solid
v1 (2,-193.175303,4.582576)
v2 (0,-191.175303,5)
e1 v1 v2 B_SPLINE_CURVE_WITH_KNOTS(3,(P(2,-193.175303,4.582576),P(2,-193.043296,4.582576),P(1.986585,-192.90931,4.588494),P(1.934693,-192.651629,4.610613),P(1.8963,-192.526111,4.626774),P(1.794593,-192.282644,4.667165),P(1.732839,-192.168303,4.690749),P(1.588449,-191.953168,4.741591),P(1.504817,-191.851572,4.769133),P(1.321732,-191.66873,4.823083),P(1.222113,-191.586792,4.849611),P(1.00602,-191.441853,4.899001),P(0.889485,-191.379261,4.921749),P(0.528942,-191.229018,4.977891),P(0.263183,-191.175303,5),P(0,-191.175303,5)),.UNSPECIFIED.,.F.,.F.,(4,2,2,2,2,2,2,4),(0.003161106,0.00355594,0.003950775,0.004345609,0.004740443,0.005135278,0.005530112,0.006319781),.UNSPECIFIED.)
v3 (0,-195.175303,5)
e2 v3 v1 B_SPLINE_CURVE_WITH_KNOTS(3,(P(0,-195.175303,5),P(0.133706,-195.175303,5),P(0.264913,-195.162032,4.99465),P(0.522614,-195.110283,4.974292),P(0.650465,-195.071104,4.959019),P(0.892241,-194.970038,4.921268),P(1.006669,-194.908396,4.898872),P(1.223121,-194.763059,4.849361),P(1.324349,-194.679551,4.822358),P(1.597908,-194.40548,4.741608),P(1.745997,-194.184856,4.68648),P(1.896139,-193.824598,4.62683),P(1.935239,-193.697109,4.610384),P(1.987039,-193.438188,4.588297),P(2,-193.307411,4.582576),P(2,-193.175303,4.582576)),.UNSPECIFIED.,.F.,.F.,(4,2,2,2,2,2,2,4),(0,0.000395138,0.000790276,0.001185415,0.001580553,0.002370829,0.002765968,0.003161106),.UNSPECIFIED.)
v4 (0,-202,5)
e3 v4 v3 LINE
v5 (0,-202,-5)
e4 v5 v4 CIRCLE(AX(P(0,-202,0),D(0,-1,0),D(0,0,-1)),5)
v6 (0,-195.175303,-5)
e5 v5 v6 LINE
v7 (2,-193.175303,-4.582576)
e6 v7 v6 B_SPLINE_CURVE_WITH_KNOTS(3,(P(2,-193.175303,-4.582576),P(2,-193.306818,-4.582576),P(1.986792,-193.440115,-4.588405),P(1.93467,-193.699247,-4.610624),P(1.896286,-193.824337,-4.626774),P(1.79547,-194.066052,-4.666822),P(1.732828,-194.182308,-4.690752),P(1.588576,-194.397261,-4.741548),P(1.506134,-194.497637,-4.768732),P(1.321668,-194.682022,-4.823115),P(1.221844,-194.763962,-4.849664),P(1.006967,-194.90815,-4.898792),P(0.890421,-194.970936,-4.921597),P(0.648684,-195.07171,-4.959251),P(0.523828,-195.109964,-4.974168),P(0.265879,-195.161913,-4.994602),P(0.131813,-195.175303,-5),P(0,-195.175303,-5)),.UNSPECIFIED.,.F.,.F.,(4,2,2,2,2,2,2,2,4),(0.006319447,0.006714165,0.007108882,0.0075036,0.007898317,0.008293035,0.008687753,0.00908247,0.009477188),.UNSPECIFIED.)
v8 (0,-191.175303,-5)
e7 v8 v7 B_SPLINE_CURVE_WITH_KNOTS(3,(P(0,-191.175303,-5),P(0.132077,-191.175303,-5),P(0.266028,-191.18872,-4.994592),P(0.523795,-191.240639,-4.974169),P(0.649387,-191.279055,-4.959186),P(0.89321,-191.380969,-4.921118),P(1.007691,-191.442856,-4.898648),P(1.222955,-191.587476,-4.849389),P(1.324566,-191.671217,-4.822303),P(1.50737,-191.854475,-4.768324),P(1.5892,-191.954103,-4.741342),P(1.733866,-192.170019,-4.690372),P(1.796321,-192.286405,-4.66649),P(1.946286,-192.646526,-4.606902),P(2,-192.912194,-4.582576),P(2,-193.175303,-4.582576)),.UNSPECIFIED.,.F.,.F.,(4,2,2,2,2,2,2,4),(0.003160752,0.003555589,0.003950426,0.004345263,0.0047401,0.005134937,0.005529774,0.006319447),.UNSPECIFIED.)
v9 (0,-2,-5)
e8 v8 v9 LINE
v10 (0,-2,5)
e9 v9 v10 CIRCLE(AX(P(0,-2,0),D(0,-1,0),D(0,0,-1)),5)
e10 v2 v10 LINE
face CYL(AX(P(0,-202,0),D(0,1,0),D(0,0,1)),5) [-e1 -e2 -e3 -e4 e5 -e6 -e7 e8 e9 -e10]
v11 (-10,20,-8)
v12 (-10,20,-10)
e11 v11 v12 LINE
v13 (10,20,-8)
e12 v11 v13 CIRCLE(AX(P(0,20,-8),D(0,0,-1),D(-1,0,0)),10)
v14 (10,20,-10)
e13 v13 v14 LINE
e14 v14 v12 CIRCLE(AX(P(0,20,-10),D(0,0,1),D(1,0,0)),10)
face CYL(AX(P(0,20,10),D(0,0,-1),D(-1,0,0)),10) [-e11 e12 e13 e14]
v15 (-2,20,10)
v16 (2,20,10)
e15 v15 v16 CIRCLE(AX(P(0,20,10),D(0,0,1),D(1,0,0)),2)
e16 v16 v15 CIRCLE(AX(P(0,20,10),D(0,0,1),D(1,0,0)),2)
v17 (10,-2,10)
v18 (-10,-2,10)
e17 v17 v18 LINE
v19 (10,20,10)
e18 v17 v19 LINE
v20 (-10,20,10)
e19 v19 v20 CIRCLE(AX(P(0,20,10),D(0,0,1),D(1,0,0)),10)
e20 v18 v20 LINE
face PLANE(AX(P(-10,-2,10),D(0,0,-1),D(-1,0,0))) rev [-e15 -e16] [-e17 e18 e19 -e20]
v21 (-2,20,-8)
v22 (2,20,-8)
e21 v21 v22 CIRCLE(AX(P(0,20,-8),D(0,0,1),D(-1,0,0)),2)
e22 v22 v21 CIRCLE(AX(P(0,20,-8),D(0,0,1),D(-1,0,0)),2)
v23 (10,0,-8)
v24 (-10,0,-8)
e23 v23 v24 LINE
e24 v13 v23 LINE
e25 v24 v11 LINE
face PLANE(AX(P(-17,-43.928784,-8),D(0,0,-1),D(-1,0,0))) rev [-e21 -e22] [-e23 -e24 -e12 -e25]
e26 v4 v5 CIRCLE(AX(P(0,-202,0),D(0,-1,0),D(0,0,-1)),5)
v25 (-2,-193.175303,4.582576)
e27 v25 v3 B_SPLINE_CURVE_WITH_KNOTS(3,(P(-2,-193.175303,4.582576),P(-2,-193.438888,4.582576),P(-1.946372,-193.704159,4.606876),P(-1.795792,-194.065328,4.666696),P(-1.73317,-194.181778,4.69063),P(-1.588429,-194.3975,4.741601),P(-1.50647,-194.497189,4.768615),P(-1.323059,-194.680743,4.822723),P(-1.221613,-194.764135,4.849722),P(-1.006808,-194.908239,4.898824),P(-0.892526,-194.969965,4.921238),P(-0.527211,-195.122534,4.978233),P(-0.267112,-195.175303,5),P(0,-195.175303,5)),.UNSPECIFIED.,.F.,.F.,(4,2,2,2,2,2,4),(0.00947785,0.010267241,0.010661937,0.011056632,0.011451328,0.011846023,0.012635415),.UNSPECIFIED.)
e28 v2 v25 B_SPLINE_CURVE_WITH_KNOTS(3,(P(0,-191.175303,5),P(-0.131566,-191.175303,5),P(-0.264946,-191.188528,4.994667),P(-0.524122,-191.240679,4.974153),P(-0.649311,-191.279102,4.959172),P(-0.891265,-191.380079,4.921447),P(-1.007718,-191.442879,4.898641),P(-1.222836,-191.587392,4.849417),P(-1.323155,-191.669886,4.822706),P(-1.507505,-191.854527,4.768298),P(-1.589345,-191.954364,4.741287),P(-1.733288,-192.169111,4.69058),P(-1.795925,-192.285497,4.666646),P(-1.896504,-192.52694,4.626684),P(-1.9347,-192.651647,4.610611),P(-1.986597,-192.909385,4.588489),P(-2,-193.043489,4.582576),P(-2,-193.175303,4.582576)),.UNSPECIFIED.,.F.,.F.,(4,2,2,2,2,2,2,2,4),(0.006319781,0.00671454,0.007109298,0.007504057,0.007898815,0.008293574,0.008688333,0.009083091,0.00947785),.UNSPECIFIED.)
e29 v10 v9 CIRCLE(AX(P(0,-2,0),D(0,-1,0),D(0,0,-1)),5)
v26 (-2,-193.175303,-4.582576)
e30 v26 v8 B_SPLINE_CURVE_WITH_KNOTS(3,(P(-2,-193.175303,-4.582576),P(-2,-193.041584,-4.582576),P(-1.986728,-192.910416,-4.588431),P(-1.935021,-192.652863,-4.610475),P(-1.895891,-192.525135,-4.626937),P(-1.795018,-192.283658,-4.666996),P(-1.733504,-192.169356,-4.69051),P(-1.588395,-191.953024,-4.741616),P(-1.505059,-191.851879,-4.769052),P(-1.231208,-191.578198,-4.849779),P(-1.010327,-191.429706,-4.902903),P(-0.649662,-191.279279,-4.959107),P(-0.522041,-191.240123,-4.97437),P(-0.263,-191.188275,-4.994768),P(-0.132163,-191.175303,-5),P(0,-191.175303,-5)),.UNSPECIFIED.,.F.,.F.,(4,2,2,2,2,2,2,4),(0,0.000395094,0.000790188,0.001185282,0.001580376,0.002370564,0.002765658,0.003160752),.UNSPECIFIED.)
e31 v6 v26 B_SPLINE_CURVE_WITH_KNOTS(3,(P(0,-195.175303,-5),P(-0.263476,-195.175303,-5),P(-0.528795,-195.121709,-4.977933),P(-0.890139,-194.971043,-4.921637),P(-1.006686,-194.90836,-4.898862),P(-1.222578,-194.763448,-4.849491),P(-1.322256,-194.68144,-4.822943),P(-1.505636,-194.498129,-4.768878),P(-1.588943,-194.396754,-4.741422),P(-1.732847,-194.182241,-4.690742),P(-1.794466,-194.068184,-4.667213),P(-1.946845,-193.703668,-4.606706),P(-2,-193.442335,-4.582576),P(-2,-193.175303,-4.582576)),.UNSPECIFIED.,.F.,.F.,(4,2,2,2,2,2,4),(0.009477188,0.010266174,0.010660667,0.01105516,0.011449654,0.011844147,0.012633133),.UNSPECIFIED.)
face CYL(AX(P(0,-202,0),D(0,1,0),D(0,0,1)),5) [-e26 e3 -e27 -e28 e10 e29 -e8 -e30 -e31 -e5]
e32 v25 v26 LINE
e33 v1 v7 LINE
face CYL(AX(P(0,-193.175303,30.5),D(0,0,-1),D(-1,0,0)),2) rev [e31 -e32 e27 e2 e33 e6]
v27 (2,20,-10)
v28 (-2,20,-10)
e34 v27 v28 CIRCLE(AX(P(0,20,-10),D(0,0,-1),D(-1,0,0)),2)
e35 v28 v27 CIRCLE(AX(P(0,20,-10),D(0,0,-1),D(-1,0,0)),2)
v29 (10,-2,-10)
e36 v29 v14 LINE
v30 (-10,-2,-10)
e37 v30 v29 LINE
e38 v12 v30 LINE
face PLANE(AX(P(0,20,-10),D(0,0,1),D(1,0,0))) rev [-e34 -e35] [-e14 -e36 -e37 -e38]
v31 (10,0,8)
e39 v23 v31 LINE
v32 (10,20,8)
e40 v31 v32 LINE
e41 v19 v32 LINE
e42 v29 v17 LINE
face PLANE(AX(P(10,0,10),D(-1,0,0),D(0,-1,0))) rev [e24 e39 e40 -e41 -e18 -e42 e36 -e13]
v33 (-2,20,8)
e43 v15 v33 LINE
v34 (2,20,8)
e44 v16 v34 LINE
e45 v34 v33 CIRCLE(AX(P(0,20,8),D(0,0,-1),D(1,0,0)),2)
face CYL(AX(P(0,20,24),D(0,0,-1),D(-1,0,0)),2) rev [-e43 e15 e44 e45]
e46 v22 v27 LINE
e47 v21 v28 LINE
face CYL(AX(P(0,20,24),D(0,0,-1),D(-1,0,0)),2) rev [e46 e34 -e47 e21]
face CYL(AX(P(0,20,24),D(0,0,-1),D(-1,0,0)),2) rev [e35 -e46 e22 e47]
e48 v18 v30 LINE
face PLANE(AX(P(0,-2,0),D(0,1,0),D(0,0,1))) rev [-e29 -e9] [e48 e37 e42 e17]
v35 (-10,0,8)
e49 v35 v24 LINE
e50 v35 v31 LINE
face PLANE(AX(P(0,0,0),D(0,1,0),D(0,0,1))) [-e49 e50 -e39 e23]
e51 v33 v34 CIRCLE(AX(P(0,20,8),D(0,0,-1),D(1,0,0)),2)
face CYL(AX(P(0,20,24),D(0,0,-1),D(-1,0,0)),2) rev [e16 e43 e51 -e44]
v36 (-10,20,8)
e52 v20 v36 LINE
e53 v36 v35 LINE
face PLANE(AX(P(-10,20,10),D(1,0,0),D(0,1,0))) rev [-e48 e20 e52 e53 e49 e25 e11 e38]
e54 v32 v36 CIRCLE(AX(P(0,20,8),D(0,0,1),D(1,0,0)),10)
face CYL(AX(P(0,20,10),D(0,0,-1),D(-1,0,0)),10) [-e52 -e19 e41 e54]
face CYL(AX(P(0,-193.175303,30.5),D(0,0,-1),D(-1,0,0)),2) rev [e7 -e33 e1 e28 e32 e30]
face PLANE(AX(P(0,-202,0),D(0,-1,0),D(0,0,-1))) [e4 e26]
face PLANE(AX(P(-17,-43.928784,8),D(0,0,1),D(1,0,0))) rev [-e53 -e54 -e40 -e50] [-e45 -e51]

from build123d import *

# Parameters (mm, degrees)
EXTRUDE_1_DEPTH     = 10
SKETCH_2_R          = 2
CUT_EXTRUDE_1_DEPTH = 34
SKETCH_3_W          = 16
SKETCH_3_H          = 87.857567692
CUT_EXTRUDE_2_DEPTH = 17
SKETCH_5_W          = 20
SKETCH_5_H          = 20
EXTRUDE_2_DEPTH     = 2
SKETCH_6_R          = 5
EXTRUDE_3_DEPTH     = 200
SKETCH_7_R          = 2
CUT_EXTRUDE_3_DEPTH = 30.5


with BuildPart() as part:
    # 草图1 → 凸台-拉伸1 (new, symmetric)
    with BuildSketch(Plane.XY):
        with BuildLine():
            Line((-10, 20), (-10, 0))
            Line((-10, 0), (10, 0))
            Line((10, 0), (10, 20))
            ThreePointArc((10, 20), (0, 30), (-10, 20))
        make_face()
    extrude(amount=EXTRUDE_1_DEPTH, both=True)

    # 草图2 → 切除-拉伸1 (cut)
    with BuildSketch(Plane(origin=(0, 0, -10), x_dir=(-1, 0, 0), z_dir=(0, 0, -1))):
        with Locations((0, 20)):
            Circle(SKETCH_2_R)
    extrude(amount=-CUT_EXTRUDE_1_DEPTH, mode=Mode.SUBTRACT)

    # 草图3 → 切除-拉伸2 (cut, symmetric)
    with BuildSketch(Plane(origin=(0, 0, 0), x_dir=(0, 0, -1), z_dir=(1, 0, 0))):
        Rectangle(SKETCH_3_W, SKETCH_3_H)
    extrude(amount=CUT_EXTRUDE_2_DEPTH, both=True, mode=Mode.SUBTRACT)


with BuildPart() as cut_extrude_2_piece_1:
    # of the separate pieces the step leaves, piece 1, a body of its own (cut_extrude_2_pieces)
    add(part.part.solids().sort_by_distance((-10, 20, -8))[0])



with BuildPart() as cut_extrude_2_piece_2:
    # of the separate pieces the step leaves, piece 2, a body of its own (cut_extrude_2_pieces)
    add(part.part.solids().sort_by_distance((-10, 20, 10))[0])


with BuildPart() as cut_extrude_2_piece_1_1:
    add(cut_extrude_2_piece_1.part)

    add(cut_extrude_2_piece_2.part)  # 凸台-拉伸2 merges 切除-拉伸2 piece 2
    # 草图5 → 凸台-拉伸2 (add)
    with BuildSketch(Plane.XZ):
        Rectangle(SKETCH_5_W, SKETCH_5_H)
    extrude(amount=EXTRUDE_2_DEPTH)

    # 草图6 → 凸台-拉伸3 (add)
    with BuildSketch(Plane.XZ.offset(2)):
        with Locations(Location((0, 0, 0), (0, 0, 270))):
            Circle(SKETCH_6_R)
    extrude(amount=EXTRUDE_3_DEPTH)

    # 草图7 → 切除-拉伸3 (cut, symmetric)
    with BuildSketch(Plane.XY):
        with Locations(Location((0, -193.17530314, 0), (0, 0, 269.999999999))):
            Circle(SKETCH_7_R)
    extrude(amount=CUT_EXTRUDE_3_DEPTH, both=True, mode=Mode.SUBTRACT)


solid = cut_extrude_2_piece_1_1.part
